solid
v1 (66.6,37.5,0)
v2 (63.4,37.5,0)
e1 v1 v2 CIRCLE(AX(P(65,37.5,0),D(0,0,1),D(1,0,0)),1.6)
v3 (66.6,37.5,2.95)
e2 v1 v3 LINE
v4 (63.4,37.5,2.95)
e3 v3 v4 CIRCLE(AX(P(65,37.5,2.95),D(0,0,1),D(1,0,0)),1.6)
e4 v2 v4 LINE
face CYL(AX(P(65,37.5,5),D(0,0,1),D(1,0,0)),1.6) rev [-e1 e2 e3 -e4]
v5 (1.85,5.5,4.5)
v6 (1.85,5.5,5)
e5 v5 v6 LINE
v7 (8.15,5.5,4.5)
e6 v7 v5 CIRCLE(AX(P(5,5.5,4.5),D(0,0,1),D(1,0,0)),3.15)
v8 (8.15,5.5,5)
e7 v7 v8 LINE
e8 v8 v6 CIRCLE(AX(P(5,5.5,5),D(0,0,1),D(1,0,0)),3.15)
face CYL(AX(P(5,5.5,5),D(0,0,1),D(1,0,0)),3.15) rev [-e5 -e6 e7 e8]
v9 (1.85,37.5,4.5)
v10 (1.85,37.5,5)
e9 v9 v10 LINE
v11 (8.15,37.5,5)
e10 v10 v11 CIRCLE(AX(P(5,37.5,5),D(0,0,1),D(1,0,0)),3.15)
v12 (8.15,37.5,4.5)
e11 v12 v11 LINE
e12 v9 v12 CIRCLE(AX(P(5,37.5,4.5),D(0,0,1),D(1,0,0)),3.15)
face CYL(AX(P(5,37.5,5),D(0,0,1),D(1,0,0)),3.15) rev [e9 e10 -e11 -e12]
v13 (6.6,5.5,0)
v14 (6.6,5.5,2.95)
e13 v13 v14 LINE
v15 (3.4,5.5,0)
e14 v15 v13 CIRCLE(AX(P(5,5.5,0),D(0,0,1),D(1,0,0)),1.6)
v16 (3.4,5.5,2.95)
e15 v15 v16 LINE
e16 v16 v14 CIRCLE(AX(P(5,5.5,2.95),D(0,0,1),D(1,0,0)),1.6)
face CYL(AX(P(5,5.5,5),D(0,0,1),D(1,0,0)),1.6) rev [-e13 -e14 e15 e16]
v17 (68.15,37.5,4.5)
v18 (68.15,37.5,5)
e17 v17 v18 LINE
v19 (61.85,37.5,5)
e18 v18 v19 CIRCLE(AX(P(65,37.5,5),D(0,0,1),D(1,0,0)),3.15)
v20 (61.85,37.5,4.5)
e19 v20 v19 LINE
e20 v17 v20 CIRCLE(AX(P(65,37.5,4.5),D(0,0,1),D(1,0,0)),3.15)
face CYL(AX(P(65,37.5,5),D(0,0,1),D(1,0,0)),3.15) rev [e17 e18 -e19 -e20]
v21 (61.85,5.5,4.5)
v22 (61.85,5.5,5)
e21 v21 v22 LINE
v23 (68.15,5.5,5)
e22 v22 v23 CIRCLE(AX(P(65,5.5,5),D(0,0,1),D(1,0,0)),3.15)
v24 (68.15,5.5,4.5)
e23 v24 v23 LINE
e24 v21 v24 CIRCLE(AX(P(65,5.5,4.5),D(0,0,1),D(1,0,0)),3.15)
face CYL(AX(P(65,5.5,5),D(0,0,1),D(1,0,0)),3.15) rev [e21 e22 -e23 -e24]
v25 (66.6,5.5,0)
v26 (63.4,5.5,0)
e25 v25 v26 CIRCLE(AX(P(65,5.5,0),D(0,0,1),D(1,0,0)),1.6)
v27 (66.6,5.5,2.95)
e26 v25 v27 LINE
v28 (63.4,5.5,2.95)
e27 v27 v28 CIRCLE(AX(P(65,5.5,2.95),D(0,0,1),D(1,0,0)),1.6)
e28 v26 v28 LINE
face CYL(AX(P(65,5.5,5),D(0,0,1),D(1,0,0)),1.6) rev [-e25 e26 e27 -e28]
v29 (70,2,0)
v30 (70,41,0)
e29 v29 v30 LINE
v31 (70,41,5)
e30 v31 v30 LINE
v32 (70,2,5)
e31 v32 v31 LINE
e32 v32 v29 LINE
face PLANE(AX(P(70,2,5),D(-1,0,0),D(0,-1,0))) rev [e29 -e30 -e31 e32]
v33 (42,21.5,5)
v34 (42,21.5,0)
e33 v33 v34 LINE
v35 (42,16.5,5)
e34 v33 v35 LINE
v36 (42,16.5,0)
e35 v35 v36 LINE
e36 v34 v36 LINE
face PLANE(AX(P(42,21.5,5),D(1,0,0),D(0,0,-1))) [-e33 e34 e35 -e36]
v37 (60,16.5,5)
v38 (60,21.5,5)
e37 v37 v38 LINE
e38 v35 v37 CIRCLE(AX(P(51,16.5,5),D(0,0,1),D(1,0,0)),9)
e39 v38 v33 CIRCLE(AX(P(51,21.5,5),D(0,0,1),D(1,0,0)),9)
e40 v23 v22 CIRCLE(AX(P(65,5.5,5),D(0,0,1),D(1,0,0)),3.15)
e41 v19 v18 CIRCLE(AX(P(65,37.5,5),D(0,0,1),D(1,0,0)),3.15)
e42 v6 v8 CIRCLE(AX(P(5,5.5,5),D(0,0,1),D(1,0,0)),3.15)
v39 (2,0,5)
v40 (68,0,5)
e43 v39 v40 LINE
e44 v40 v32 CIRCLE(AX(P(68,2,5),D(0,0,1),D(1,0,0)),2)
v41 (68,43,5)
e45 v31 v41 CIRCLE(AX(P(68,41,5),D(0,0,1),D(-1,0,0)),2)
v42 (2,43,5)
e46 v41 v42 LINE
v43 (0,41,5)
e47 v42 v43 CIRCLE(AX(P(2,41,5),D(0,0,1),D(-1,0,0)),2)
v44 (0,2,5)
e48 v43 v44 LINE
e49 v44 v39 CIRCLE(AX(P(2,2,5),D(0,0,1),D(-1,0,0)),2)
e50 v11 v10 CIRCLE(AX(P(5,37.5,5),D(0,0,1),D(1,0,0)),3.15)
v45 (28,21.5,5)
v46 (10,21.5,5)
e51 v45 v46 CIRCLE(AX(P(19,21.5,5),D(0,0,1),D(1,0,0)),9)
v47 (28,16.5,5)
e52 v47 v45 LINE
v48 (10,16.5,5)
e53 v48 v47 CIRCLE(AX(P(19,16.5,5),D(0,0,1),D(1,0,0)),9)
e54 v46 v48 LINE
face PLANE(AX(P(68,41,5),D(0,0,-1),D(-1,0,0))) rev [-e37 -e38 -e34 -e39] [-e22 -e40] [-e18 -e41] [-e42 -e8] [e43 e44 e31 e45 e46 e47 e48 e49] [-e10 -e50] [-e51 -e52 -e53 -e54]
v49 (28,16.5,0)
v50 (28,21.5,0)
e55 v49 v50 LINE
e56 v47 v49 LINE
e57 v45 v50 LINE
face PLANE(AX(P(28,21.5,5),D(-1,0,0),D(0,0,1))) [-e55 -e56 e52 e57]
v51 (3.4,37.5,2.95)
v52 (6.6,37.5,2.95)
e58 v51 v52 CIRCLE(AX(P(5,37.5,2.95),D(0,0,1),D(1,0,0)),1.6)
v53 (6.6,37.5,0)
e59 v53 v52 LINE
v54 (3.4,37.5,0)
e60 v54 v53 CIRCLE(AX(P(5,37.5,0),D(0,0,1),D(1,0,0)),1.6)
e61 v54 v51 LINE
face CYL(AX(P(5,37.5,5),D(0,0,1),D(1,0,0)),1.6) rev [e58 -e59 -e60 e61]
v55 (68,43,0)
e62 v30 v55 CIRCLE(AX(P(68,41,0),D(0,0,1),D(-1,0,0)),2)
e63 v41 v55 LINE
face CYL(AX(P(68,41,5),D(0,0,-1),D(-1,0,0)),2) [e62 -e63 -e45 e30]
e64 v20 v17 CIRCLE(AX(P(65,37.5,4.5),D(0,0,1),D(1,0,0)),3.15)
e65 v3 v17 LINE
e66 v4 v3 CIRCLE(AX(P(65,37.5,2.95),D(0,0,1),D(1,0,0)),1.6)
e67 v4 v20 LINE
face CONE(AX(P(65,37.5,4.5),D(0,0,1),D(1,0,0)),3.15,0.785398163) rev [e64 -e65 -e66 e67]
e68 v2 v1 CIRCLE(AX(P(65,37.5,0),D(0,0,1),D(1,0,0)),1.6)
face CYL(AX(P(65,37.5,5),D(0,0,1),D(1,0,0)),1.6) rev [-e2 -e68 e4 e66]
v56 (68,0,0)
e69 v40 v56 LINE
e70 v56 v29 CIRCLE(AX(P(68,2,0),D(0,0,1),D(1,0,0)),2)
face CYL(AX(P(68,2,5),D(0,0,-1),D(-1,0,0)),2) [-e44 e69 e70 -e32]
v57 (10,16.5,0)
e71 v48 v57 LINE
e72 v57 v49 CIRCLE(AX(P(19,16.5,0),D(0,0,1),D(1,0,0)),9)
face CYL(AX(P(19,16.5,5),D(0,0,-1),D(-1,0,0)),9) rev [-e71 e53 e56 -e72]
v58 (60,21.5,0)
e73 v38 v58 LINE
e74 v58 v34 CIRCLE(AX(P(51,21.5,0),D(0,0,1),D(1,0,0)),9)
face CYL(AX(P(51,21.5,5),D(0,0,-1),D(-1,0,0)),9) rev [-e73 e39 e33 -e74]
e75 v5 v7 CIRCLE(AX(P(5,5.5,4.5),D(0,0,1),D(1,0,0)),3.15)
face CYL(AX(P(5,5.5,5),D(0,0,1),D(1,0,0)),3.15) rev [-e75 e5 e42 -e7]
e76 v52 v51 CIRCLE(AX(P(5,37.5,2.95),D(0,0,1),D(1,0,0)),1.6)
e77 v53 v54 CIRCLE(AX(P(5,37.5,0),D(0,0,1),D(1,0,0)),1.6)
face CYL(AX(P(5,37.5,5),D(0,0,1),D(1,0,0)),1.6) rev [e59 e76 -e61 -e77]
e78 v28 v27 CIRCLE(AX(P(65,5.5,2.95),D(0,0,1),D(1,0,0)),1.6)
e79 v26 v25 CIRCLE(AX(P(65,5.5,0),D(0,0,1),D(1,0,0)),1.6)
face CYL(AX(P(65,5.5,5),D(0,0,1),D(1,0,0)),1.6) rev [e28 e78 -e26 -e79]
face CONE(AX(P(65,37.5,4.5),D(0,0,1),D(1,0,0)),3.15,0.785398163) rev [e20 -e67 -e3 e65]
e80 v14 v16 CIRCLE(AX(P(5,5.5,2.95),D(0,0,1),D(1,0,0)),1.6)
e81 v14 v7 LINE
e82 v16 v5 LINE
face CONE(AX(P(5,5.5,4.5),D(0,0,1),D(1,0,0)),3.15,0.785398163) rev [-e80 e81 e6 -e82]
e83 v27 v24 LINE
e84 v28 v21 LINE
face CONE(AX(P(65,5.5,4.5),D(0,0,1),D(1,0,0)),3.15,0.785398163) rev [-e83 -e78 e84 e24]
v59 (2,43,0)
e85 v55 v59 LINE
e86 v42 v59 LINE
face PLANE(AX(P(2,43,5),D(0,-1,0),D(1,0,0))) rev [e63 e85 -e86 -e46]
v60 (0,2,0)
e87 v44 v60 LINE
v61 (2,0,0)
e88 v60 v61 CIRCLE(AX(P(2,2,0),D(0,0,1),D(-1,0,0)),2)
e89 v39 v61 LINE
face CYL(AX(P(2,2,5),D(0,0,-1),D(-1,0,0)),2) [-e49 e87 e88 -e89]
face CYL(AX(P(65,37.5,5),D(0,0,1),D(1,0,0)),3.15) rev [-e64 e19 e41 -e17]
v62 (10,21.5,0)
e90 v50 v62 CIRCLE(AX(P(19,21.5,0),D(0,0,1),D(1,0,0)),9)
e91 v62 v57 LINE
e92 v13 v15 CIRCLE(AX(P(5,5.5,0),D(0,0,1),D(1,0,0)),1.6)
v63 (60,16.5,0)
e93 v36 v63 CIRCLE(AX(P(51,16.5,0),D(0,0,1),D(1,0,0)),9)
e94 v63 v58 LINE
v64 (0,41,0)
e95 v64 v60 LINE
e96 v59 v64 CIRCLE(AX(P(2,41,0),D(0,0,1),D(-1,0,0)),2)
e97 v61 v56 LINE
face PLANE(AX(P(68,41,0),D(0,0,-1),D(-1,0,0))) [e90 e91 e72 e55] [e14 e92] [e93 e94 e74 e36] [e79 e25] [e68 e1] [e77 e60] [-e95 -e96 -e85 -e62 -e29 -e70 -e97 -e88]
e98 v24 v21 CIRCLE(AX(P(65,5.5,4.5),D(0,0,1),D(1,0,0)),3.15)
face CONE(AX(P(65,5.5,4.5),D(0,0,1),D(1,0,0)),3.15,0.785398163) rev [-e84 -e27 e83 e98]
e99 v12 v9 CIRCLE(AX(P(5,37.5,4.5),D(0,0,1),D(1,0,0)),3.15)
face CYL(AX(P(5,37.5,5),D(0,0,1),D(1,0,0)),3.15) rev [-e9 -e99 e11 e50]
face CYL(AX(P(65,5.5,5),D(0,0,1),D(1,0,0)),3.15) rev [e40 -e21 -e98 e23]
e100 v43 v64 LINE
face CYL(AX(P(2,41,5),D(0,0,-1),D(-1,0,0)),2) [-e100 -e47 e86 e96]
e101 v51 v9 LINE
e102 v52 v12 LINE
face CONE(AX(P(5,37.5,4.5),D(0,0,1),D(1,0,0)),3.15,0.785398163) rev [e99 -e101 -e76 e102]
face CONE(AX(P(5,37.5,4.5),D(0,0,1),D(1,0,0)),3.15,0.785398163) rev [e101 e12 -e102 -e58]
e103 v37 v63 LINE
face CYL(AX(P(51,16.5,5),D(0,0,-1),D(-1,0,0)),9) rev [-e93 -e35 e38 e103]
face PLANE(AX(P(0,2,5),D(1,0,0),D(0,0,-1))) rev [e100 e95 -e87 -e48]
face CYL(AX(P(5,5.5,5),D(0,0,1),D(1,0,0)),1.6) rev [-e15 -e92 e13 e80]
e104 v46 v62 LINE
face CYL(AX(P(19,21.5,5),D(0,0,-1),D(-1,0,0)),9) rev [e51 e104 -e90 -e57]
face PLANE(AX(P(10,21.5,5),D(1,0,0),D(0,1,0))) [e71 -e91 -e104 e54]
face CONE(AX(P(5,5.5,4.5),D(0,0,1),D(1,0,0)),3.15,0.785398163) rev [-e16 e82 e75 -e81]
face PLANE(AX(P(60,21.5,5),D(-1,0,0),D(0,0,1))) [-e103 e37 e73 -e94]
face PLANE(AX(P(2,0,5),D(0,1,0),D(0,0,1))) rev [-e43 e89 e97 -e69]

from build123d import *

# Parameters (mm, degrees)
BOSS_EXTRUDE1_DEPTH                            = 5
CSK_FOR_M3_FLAT_HEAD_MACHINE_SCREW1_AT_2_COUNT = 2
CSK_FOR_M3_FLAT_HEAD_MACHINE_SCREW1_AT_2_PITCH = 32
CSK_FOR_M3_FLAT_HEAD_MACHINE_SCREW1_AT_3_COUNT = 2
CSK_FOR_M3_FLAT_HEAD_MACHINE_SCREW1_AT_3_PITCH = 68
CSK_FOR_M3_FLAT_HEAD_MACHINE_SCREW1_AT_4_COUNT = 2
CSK_FOR_M3_FLAT_HEAD_MACHINE_SCREW1_AT_4_PITCH = 60


with BuildPart() as part:
    # Sketch1 → Boss-Extrude1 (new body)
    with BuildSketch(Plane.XY):
        with BuildLine():
            Line((2, 0), (68, 0))
            ThreePointArc((68, 0), (69.414213562, 0.585786438), (70, 2))
            Line((70, 2), (70, 41))
            ThreePointArc((70, 41), (69.414213562, 42.414213562), (68, 43))
            Line((68, 43), (2, 43))
            ThreePointArc((2, 43), (0.585786438, 42.414213562), (0, 41))
            Line((0, 41), (0, 2))
            ThreePointArc((0, 2), (0.585786438, 0.585786438), (2, 0))
        make_face()
        with BuildLine():
            Line((28, 21.5), (28, 16.5))
            ThreePointArc((28, 16.5), (19, 7.5), (10, 16.5))
            Line((10, 16.5), (10, 21.5))
            ThreePointArc((10, 21.5), (19, 30.5), (28, 21.5))
        make_face(mode=Mode.SUBTRACT)
        with BuildLine():
            Line((60, 21.5), (60, 16.5))
            ThreePointArc((60, 16.5), (51, 7.5), (42, 16.5))
            Line((42, 16.5), (42, 21.5))
            ThreePointArc((42, 21.5), (51, 30.5), (60, 21.5))
        make_face(mode=Mode.SUBTRACT)
    extrude(amount=BOSS_EXTRUDE1_DEPTH)

    # Sketch2 → CSK for M3 Flat Head Machine Screw1 (revolve, cut)
    with BuildSketch(Plane(origin=(5, 37.5, 5), x_dir=(0, -1, 0), z_dir=(1, 0, 0))):
        Polygon((0, 0), (0, 5), (1.6, 5), (1.6, 2.05), (3.15, 0.5), (3.15, 0), align=None)
    csk_for_m3_flat_head_machine_screw1 = revolve(axis=Axis((5, 37.5, 11.35), (0, 0, -1)), mode=Mode.SUBTRACT)

    # CSK for M3 Flat Head Machine Screw1 at 2: CSK for M3 Flat Head Machine Screw1 ×2
    with Locations(*[(0, -i * CSK_FOR_M3_FLAT_HEAD_MACHINE_SCREW1_AT_2_PITCH, 0) for i in range(1, CSK_FOR_M3_FLAT_HEAD_MACHINE_SCREW1_AT_2_COUNT)]):
        add(csk_for_m3_flat_head_machine_screw1, mode=Mode.SUBTRACT)

    # CSK for M3 Flat Head Machine Screw1 at 3: CSK for M3 Flat Head Machine Screw1 ×2
    with Locations(*[Vector(0.8823529411764707, -0.47058823529411764, 0) * (i * CSK_FOR_M3_FLAT_HEAD_MACHINE_SCREW1_AT_3_PITCH) for i in range(1, CSK_FOR_M3_FLAT_HEAD_MACHINE_SCREW1_AT_3_COUNT)]):
        add(csk_for_m3_flat_head_machine_screw1, mode=Mode.SUBTRACT)

    # CSK for M3 Flat Head Machine Screw1 at 4: CSK for M3 Flat Head Machine Screw1 ×2
    with Locations(*[(i * CSK_FOR_M3_FLAT_HEAD_MACHINE_SCREW1_AT_4_PITCH, 0, 0) for i in range(1, CSK_FOR_M3_FLAT_HEAD_MACHINE_SCREW1_AT_4_COUNT)]):
        add(csk_for_m3_flat_head_machine_screw1, mode=Mode.SUBTRACT)


solid = part.part
